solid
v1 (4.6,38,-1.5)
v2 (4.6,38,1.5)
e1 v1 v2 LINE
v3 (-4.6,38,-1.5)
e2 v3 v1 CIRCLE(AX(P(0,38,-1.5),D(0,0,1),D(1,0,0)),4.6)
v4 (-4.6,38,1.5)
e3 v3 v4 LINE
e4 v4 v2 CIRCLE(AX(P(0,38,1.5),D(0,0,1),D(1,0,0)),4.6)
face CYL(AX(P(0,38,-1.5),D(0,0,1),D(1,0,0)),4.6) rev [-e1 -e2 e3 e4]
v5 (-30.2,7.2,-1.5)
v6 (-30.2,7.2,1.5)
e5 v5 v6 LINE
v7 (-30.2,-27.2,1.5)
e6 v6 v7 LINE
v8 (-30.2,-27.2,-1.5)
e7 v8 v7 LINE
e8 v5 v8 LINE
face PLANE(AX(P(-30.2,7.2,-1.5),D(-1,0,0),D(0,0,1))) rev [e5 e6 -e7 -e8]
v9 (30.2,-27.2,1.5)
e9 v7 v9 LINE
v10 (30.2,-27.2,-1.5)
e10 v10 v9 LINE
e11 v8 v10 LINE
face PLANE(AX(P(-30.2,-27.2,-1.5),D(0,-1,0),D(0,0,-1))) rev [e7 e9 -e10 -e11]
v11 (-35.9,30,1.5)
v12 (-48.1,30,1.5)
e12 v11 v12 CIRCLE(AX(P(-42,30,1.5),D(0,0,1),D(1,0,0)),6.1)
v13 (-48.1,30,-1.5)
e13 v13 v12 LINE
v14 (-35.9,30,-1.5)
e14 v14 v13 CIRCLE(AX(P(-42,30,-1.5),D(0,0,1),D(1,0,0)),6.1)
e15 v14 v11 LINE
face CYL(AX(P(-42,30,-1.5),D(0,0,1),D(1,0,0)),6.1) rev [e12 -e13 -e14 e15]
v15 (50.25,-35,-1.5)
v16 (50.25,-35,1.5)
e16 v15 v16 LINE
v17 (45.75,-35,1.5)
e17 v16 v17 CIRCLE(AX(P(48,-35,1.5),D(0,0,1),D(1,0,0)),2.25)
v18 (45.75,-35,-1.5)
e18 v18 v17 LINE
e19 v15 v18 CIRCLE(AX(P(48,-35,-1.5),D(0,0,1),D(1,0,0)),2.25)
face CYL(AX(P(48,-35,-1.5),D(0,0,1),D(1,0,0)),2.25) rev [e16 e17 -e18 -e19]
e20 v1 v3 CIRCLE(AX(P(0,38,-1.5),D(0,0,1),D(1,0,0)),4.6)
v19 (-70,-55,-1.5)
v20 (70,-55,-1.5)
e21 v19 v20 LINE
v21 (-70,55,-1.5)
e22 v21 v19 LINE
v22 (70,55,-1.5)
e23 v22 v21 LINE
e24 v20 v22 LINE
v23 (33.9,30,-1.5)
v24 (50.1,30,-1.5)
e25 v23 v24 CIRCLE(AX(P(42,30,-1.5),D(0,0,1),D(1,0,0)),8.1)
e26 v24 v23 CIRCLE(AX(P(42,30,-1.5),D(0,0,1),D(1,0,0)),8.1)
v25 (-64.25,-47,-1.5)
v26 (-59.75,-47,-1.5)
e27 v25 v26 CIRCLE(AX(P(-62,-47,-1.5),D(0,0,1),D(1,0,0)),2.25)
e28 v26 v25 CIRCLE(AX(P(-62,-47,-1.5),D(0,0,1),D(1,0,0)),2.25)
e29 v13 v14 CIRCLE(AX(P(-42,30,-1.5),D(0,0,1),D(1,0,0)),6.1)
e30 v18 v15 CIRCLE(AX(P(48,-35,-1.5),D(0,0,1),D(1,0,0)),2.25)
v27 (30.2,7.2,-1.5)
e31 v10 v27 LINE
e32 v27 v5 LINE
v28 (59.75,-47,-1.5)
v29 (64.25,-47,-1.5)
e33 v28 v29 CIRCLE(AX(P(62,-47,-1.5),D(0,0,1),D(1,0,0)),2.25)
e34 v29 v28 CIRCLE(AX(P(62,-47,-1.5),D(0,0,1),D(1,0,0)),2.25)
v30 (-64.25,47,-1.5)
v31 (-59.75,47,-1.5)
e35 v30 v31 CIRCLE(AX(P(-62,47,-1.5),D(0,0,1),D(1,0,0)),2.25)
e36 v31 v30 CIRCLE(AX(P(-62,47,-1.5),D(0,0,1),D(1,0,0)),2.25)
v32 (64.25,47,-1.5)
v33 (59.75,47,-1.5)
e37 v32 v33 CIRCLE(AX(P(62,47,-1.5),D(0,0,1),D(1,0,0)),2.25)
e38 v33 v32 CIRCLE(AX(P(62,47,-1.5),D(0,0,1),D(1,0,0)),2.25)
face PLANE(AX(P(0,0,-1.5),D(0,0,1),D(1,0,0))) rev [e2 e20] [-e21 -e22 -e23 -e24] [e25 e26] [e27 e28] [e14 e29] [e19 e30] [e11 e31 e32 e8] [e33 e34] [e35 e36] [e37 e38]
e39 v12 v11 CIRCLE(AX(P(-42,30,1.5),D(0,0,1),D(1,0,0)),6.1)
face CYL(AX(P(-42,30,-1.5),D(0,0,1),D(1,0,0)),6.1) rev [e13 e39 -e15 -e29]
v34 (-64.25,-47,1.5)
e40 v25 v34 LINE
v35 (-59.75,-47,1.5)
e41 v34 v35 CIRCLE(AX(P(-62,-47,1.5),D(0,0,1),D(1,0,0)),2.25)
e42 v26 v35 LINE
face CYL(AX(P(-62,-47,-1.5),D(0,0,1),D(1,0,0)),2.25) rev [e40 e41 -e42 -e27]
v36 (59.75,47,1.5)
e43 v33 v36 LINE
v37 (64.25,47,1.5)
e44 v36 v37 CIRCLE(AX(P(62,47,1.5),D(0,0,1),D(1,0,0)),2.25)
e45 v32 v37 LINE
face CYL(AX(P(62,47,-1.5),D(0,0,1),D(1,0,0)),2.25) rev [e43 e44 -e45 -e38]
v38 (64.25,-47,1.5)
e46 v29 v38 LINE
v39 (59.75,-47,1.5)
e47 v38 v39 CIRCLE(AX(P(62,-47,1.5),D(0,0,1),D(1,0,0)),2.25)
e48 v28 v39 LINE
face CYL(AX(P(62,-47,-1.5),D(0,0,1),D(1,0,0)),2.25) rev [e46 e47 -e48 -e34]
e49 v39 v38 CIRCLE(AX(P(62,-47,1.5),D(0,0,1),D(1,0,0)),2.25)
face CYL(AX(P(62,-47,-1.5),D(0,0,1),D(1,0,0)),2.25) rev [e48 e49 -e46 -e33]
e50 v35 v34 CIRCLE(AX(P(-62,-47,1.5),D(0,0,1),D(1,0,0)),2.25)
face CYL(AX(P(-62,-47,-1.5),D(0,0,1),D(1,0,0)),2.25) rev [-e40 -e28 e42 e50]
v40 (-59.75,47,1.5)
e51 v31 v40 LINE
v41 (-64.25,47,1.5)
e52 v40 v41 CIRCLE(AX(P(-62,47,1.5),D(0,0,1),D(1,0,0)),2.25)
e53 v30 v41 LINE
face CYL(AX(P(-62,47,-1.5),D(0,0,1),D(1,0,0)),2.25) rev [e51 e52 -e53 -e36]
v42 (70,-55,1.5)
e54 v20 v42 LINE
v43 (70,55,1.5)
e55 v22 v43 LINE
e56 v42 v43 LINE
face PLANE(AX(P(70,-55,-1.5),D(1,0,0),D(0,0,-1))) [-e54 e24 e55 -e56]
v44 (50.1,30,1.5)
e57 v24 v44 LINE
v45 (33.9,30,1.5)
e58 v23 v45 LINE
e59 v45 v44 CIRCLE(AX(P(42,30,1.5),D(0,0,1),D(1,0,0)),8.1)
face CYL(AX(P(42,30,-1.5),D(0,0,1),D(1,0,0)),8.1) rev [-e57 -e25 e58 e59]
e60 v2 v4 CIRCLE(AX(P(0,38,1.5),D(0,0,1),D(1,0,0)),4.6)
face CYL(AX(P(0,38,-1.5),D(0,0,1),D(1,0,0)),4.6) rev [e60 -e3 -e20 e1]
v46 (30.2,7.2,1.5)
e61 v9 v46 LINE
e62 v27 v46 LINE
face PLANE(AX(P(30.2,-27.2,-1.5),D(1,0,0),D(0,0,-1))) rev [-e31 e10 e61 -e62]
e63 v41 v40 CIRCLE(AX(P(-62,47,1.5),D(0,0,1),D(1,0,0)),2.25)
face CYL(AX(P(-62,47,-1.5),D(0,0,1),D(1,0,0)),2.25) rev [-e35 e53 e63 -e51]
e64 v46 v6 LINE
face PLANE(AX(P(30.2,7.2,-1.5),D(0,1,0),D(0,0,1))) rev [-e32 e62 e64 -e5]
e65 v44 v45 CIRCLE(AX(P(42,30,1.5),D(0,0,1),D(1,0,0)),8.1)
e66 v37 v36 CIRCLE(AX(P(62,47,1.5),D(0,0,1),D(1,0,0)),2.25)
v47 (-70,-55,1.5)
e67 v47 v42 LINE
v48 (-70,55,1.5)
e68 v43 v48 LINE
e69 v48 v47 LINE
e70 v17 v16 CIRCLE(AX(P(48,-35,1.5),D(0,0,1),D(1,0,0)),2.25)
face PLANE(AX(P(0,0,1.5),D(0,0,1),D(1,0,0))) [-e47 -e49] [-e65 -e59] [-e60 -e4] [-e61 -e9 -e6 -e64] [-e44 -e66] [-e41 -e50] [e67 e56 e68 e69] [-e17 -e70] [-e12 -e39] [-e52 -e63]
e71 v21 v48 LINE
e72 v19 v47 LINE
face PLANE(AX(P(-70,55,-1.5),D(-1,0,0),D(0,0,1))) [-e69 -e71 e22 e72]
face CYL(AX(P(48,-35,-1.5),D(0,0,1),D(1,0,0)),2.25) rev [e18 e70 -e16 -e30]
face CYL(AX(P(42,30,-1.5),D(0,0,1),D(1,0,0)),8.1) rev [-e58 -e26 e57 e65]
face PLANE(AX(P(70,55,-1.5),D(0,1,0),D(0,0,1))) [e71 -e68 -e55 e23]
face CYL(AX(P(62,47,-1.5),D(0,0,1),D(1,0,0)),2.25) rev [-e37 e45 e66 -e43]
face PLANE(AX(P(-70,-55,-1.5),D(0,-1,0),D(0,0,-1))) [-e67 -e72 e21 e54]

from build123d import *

# Parameters (mm, degrees)
SKETCH_1_W      = 140
SKETCH_1_H      = 110
SKETCH_1_R      = 2.25
SKETCH_1_R_2    = 6.1
SKETCH_1_R_3    = 8.1
SKETCH_1_R_4    = 4.6
SKETCH_1_W_2    = 60.4
SKETCH_1_H_2    = 34.4
EXTRUDE_1_DEPTH = 1.5


with BuildPart() as part:
    # 草图1 → 凸台-拉伸1 (new, symmetric)
    with BuildSketch(Plane.XY):
        Rectangle(SKETCH_1_W, SKETCH_1_H)
        with Locations((-62, -47)):
            Circle(SKETCH_1_R, mode=Mode.SUBTRACT)
        with Locations((-62, 47)):
            Circle(SKETCH_1_R, mode=Mode.SUBTRACT)
        with Locations((62, -47)):
            Circle(SKETCH_1_R, mode=Mode.SUBTRACT)
        with Locations((62, 47)):
            Circle(SKETCH_1_R, mode=Mode.SUBTRACT)
        with Locations((-42, 30)):
            Circle(SKETCH_1_R_2, mode=Mode.SUBTRACT)
        with Locations((42, 30)):
            Circle(SKETCH_1_R_3, mode=Mode.SUBTRACT)
        with Locations((0, 38)):
            Circle(SKETCH_1_R_4, mode=Mode.SUBTRACT)
        with Locations((48, -35)):
            Circle(SKETCH_1_R, mode=Mode.SUBTRACT)
        with Locations((0, -10)):
            Rectangle(SKETCH_1_W_2, SKETCH_1_H_2, mode=Mode.SUBTRACT)
    extrude(amount=EXTRUDE_1_DEPTH, both=True)


solid = part.part
